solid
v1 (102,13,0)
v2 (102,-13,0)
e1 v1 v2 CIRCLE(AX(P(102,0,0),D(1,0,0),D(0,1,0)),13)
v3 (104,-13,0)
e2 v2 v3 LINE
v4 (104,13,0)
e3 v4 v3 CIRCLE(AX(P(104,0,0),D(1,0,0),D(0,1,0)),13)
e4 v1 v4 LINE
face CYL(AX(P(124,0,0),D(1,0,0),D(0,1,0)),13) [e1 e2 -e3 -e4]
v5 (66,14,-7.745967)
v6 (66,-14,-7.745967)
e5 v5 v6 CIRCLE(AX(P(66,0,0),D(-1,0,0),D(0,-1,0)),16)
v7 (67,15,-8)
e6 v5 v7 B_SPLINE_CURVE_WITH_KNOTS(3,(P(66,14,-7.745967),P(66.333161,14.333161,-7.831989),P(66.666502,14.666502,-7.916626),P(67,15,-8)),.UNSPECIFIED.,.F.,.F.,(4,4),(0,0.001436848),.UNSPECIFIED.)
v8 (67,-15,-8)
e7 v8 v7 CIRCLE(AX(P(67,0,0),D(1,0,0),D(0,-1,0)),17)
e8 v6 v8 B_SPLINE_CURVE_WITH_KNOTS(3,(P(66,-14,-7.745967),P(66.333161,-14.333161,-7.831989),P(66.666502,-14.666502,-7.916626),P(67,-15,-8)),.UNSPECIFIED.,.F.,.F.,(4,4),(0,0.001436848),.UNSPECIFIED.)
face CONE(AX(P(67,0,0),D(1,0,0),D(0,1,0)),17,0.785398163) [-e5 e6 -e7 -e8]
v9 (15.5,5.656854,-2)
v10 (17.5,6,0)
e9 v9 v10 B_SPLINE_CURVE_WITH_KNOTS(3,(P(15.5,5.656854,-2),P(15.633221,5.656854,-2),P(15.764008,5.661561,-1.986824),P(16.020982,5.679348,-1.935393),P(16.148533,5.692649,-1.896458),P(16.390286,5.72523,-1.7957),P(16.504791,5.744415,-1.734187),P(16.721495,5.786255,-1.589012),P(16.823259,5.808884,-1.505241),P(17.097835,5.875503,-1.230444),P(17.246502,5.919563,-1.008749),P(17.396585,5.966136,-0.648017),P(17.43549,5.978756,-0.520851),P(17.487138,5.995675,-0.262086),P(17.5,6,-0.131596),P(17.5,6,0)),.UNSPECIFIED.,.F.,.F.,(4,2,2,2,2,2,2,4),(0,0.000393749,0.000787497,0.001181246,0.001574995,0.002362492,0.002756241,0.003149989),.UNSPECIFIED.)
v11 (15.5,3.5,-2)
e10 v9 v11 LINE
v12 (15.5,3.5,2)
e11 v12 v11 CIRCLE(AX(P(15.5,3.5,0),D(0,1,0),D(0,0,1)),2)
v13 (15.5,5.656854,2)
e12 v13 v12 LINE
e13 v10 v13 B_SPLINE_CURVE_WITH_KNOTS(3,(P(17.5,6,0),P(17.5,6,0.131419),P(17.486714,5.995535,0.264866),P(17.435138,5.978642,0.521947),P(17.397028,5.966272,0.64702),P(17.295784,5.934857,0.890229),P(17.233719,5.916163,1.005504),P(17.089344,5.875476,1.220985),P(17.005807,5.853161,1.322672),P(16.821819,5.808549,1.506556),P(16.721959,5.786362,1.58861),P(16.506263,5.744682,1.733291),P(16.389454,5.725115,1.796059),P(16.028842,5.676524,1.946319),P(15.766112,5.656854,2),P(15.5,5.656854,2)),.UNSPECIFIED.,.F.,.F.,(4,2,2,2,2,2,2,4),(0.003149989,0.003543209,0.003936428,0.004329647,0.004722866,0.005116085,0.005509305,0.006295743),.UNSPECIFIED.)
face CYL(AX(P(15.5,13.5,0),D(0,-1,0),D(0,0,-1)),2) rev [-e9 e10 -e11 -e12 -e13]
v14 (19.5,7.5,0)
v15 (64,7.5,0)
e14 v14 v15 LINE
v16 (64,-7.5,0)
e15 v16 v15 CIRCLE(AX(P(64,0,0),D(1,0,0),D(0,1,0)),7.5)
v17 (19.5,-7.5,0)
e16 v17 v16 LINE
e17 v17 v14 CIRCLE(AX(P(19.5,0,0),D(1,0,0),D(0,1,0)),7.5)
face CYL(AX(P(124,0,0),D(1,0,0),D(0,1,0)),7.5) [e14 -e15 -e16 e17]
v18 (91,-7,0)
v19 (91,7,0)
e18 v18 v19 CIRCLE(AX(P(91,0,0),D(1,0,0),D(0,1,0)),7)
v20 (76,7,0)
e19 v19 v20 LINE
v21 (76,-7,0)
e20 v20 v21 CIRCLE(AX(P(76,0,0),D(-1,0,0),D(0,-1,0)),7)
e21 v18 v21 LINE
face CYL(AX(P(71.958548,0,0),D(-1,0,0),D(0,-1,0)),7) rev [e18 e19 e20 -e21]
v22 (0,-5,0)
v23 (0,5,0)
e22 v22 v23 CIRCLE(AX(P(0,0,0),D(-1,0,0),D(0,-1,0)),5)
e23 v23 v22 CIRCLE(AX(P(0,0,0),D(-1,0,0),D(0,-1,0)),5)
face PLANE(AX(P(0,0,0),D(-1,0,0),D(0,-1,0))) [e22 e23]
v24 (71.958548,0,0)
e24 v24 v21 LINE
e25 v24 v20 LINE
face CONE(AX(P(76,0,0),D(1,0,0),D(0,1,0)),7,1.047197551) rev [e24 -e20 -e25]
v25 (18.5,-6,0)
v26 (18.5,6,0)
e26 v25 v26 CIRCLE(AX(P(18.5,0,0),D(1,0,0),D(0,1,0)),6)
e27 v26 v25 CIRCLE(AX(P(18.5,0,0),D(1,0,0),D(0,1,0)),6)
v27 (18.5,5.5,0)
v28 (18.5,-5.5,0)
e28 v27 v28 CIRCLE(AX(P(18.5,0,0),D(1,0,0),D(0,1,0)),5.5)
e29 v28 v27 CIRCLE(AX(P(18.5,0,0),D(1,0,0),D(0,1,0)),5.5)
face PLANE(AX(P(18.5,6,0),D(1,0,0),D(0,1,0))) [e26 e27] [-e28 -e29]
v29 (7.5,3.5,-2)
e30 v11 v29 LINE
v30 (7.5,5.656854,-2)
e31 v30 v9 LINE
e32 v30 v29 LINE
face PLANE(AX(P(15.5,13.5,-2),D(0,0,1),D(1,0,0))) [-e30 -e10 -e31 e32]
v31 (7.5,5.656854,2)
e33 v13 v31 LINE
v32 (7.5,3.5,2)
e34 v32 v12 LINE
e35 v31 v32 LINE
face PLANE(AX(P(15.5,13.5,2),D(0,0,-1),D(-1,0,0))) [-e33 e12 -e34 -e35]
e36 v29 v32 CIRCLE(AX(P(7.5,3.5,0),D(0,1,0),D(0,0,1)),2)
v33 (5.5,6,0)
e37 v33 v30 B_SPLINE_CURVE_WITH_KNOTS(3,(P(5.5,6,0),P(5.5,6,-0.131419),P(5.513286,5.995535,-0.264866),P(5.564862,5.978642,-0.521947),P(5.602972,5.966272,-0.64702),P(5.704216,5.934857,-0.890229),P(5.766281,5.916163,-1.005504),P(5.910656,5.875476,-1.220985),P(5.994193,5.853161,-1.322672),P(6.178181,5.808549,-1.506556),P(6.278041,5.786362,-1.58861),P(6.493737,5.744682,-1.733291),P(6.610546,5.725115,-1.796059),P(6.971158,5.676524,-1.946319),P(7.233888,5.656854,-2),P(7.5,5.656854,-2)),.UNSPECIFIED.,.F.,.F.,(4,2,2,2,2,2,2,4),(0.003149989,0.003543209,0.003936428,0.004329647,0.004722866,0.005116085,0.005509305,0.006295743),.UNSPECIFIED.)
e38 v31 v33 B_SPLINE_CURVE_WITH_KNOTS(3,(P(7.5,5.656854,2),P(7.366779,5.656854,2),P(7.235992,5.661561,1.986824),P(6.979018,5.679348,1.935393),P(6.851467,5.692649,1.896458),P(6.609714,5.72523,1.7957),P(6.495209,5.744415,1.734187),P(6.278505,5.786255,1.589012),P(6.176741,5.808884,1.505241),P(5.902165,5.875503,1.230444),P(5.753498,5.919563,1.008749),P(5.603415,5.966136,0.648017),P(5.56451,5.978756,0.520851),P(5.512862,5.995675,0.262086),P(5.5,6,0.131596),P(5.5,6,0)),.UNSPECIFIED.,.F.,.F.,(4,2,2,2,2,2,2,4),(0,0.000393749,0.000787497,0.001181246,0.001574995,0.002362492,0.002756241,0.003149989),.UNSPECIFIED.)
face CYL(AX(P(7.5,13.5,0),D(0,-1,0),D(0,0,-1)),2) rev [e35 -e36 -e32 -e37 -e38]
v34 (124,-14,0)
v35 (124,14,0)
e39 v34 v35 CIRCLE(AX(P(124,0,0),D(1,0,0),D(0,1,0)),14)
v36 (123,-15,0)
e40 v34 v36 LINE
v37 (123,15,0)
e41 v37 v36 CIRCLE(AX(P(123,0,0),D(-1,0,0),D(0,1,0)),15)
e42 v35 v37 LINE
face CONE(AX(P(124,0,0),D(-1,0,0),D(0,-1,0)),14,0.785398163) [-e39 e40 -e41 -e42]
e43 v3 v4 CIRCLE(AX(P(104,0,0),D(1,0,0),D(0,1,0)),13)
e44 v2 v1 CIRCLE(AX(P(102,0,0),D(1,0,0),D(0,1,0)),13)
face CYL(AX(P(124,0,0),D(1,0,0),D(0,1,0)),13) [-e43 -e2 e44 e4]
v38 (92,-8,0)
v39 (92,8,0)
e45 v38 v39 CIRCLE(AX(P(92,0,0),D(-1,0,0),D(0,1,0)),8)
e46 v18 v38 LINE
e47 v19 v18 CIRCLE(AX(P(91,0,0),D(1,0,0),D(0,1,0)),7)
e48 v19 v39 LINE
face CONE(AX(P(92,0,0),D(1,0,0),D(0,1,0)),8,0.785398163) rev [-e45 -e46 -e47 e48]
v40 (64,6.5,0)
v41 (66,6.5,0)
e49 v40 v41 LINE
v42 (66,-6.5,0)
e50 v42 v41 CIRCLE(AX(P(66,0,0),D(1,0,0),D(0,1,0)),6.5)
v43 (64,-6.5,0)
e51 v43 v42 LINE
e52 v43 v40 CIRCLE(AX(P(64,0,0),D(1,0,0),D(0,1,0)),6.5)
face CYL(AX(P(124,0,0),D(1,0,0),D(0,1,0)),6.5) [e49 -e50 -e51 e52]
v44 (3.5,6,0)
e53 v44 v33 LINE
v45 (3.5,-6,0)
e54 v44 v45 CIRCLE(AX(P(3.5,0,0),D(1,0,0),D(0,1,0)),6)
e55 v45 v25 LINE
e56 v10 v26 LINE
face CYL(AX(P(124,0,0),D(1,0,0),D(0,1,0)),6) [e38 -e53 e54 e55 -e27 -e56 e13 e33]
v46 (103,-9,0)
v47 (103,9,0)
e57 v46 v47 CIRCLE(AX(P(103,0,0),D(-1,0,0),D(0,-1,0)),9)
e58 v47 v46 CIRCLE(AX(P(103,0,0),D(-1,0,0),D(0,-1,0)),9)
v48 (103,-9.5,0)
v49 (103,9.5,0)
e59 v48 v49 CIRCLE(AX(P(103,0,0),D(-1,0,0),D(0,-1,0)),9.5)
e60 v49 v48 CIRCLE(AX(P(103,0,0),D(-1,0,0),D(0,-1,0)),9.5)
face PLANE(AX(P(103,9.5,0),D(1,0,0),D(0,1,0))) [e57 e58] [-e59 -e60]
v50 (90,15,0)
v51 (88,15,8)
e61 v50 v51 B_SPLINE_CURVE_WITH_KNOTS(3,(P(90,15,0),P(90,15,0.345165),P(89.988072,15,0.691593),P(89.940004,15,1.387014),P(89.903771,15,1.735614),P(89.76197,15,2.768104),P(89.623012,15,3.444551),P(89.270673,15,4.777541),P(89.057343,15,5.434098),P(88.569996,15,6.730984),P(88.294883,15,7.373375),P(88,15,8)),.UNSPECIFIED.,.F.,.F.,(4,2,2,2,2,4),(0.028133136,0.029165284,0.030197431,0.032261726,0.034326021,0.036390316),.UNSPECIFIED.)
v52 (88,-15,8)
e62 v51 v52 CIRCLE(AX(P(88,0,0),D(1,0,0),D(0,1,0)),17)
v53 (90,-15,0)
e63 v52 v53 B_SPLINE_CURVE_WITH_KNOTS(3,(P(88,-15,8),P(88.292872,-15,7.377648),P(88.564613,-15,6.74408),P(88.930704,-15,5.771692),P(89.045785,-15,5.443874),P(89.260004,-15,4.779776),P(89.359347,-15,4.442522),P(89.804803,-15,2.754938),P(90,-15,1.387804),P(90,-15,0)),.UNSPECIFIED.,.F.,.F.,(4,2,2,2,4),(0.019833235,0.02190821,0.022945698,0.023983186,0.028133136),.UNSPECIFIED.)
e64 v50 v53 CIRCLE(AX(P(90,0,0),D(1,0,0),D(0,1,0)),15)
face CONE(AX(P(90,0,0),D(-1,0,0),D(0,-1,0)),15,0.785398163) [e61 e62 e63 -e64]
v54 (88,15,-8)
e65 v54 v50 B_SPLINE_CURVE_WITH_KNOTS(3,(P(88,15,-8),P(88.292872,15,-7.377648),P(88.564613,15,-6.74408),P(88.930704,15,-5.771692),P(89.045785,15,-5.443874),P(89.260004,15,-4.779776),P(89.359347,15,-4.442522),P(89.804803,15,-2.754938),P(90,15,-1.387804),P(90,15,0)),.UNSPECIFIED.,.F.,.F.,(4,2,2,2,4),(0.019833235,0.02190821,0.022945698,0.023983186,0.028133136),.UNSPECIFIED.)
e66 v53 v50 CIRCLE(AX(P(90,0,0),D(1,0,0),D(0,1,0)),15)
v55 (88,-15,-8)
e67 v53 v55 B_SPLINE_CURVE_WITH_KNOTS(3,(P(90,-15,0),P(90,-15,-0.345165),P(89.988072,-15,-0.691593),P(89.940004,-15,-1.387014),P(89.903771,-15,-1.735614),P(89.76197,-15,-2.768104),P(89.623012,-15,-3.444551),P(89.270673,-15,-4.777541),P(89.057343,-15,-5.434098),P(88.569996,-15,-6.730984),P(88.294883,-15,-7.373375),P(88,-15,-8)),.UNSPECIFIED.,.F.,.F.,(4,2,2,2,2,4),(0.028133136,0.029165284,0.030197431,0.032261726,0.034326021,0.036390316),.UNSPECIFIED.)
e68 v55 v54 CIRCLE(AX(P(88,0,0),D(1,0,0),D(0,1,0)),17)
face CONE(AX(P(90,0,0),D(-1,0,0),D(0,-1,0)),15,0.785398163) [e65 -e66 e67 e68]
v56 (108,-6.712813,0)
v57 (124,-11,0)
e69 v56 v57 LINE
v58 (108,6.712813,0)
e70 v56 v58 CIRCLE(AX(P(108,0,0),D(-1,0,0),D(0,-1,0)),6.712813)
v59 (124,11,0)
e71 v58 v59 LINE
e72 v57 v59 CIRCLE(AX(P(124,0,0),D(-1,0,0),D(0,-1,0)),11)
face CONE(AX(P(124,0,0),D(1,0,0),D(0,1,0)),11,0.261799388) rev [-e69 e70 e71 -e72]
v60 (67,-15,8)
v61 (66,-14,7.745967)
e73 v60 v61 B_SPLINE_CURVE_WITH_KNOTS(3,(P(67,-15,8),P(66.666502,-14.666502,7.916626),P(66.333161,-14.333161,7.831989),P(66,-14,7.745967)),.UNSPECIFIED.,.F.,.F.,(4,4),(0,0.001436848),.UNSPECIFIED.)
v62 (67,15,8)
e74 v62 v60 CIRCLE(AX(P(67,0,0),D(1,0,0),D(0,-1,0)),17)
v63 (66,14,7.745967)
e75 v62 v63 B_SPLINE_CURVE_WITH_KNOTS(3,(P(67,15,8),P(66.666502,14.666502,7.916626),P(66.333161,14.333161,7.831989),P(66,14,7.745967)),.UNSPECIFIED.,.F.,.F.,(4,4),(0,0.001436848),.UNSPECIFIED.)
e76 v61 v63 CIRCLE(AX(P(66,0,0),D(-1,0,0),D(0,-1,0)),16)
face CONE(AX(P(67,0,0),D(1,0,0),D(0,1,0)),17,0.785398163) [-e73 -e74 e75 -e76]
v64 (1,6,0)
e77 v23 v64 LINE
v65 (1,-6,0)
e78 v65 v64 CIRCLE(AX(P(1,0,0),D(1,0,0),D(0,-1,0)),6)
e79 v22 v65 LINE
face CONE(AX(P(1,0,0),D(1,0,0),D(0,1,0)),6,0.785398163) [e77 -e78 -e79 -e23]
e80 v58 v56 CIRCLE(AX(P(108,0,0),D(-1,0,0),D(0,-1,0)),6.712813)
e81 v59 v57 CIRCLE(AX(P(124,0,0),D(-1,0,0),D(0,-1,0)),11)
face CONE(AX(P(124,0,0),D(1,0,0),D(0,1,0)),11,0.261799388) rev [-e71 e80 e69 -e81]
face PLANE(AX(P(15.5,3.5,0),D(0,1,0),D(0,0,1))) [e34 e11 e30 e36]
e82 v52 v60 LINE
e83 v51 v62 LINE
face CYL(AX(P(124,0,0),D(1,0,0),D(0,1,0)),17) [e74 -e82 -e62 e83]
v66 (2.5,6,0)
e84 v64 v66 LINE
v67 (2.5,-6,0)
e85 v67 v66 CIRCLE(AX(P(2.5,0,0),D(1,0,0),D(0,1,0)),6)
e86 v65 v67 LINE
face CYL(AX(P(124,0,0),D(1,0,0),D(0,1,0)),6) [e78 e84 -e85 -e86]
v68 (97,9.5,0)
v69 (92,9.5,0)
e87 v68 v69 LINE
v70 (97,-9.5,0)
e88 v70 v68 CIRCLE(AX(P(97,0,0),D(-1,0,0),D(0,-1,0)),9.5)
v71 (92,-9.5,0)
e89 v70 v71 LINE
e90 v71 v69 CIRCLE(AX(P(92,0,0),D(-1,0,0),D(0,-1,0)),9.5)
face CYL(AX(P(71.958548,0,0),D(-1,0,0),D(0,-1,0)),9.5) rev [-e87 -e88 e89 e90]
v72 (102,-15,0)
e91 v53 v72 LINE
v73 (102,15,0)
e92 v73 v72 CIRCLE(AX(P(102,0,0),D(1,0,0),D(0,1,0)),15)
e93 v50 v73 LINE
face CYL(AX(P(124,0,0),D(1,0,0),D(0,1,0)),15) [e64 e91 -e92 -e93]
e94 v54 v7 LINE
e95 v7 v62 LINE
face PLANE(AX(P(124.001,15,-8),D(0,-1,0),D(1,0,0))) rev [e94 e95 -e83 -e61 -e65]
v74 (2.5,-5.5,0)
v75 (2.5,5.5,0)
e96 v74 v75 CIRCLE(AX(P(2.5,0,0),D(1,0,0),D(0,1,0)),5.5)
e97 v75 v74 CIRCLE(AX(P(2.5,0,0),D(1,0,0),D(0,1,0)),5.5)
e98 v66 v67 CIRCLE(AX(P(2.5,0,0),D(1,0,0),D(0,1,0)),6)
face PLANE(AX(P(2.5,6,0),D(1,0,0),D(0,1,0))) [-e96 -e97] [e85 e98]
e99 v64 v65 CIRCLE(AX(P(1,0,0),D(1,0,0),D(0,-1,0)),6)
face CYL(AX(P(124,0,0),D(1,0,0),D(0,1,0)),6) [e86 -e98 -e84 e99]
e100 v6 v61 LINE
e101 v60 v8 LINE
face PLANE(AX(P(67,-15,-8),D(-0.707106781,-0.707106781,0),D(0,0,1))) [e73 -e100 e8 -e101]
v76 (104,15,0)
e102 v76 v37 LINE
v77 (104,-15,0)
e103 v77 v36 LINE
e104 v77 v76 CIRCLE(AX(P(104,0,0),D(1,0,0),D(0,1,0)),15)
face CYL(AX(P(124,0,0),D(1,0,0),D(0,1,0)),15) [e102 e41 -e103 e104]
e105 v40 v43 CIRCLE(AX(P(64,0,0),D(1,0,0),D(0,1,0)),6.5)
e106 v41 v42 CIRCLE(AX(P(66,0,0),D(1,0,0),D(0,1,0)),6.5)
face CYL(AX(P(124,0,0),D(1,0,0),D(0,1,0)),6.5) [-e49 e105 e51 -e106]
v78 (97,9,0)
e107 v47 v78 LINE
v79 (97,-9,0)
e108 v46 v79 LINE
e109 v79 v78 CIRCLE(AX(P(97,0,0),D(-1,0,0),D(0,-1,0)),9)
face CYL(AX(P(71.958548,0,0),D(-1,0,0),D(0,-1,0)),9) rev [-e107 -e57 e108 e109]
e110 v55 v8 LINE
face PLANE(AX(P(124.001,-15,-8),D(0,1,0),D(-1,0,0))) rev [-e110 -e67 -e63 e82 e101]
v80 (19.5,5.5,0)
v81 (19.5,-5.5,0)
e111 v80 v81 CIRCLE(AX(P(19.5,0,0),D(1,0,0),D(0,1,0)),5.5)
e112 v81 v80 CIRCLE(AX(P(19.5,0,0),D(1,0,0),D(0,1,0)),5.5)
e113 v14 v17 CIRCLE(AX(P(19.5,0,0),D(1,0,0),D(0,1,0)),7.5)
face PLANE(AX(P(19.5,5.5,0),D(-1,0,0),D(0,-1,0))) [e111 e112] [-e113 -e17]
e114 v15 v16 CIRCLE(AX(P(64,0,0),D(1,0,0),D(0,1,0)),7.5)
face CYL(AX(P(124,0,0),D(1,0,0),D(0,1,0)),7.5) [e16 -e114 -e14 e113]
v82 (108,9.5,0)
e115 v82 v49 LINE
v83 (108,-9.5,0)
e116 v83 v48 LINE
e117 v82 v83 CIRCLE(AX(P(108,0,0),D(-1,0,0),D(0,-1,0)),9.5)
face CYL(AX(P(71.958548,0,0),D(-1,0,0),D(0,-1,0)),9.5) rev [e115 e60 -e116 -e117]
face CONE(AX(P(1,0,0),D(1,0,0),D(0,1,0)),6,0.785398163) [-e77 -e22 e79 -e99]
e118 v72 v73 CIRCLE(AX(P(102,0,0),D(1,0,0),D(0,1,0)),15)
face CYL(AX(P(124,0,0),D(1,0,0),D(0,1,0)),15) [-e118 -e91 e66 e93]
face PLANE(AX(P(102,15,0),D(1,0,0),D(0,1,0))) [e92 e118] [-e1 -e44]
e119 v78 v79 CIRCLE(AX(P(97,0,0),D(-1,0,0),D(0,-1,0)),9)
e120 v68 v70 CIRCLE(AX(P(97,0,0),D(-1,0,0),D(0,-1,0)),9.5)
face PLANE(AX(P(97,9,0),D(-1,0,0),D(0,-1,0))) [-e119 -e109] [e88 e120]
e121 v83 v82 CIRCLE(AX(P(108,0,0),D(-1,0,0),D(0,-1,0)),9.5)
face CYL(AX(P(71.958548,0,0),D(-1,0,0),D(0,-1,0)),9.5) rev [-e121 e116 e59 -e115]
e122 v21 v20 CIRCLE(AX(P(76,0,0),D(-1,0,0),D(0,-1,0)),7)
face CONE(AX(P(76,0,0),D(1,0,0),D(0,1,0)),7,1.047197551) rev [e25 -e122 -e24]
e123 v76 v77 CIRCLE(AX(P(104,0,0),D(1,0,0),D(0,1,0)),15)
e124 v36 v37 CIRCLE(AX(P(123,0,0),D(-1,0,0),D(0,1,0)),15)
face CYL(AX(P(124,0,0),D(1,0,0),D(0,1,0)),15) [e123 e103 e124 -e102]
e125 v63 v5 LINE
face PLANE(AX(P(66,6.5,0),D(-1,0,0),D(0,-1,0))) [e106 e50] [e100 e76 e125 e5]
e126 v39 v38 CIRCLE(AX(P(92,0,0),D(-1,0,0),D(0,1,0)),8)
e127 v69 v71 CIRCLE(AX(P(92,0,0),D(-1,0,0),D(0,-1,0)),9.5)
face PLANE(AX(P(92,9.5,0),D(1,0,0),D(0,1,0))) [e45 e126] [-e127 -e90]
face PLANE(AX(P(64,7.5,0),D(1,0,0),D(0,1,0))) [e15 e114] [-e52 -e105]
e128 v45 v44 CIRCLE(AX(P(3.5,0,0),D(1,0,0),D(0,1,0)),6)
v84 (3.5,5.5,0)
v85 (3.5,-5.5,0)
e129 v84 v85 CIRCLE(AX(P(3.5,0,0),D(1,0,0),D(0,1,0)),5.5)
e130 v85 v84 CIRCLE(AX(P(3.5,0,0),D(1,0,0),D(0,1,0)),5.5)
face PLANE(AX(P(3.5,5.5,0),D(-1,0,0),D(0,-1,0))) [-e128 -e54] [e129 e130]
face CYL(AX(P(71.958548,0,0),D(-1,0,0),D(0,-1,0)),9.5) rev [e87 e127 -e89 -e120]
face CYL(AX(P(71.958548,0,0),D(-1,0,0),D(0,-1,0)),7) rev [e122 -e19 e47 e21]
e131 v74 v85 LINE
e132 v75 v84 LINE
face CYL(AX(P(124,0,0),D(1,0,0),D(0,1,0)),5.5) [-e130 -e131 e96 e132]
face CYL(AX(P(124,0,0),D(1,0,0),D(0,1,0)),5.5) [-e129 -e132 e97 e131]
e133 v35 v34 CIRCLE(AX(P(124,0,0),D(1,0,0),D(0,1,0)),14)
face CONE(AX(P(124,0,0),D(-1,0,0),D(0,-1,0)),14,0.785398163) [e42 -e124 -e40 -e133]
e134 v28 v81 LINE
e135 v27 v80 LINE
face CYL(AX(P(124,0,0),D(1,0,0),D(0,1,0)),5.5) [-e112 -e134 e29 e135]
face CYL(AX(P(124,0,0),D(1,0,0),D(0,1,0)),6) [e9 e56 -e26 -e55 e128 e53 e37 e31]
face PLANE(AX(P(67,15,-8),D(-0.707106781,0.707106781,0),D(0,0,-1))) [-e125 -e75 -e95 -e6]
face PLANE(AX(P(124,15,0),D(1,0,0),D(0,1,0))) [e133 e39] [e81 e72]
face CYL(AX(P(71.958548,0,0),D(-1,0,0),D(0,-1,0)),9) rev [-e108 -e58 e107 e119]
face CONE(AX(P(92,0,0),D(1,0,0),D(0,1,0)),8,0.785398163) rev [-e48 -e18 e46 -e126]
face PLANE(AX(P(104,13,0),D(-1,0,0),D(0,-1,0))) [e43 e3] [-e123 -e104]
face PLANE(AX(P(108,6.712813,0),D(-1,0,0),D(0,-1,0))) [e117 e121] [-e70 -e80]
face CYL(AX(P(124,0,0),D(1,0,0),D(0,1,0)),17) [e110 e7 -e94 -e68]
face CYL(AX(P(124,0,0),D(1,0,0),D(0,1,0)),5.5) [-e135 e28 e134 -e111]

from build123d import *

# Parameters (mm, degrees)
CUT_EXTRUDE1_START = 3.5
CUT_EXTRUDE1_DEPTH = 10
CUT_EXTRUDE2_REACH = 72.242
CHAMFER1_SIZE      = 1
CHAMFER2_SIZE      = 1


with BuildPart() as part:
    # Sketch1 → Revolve1 (revolve)
    with BuildSketch(Plane.XY):
        Polygon((0, 0), (0, 6), (2.5, 6), (2.5, 5.5), (3.5, 5.5), (3.5, 6), (18.5, 6), (18.5, 5.5), (19.5, 5.5), (19.5, 7.5), (64, 7.5), (64, 6.5), (66, 6.5), (66, 17), (88, 17), (90, 15), (102, 15), (102, 13), (104, 13), (104, 15), (124, 15), (124, 0), align=None)
    revolve(axis=Axis((124, 0, 0), (-1, 0, 0)))

    # Sketch3 → Cut-Extrude1 (cut)
    with BuildSketch(Plane(origin=(0, 0, 0), x_dir=(1, 0, 0), z_dir=(0, 1, 0)).offset(CUT_EXTRUDE1_START)):
        with BuildLine():
            Line((15.5, -2), (7.5, -2))
            ThreePointArc((7.5, -2), (5.5, 0), (7.5, 2))
            Line((7.5, 2), (15.5, 2))
            ThreePointArc((15.5, 2), (17.5, 0), (15.5, -2))
        make_face()
    extrude(amount=CUT_EXTRUDE1_DEPTH, mode=Mode.SUBTRACT)

    # Cut-Extrude2: up to this cone (the profile starts inside it)
    cut_extrude2_end = Plane(origin=(66, 0, 0), z_dir=(-1, 0, 0)).offset(-38.999999) * Cone(1e-06, 150.742, 150.741999, align=(Align.CENTER, Align.CENTER, Align.MIN), mode=Mode.PRIVATE)
    # Sketch6 → Cut-Extrude2 (cut, up to the surface)
    with BuildSketch(Plane.ZY.offset(-66), mode=Mode.PRIVATE) as cut_extrude2_sk1:
        with BuildLine():
            Line((-8, 15), (8, 15))
            ThreePointArc((8, 15), (0, 17), (-8, 15))
        make_face()
    cut_extrude2_tool1 = extrude(cut_extrude2_sk1.sketch, amount=-CUT_EXTRUDE2_REACH, mode=Mode.PRIVATE) & cut_extrude2_end
    add(cut_extrude2_tool1.solids().sort_by_distance((66, 15.804176, 0))[0], mode=Mode.SUBTRACT)
    # Sketch6 → Cut-Extrude2 (cut, up to the surface)
    with BuildSketch(Plane.ZY.offset(-66), mode=Mode.PRIVATE) as cut_extrude2_sk2:
        with BuildLine():
            Line((-8, -15), (8, -15))
            ThreePointArc((8, -15), (0, -17), (-8, -15))
        make_face()
    cut_extrude2_tool2 = extrude(cut_extrude2_sk2.sketch, amount=-CUT_EXTRUDE2_REACH, mode=Mode.PRIVATE) & cut_extrude2_end
    add(cut_extrude2_tool2.solids().sort_by_distance((66, -15.804176, 0))[0], mode=Mode.SUBTRACT)

    # Chamfer1
    chamfer1_edges = [part.edges().sort_by_distance(p)[0] for p in [
        (124, -15, 0),
        (66, 0, 17),
        (0, -6, 0),
        (66, 0, -17),
        (66, 15, 0),
        (66, -15, 0),
    ]]
    chamfer(chamfer1_edges, length=CHAMFER1_SIZE)

    # Sketch7 → Cut-Revolve1 (revolve, cut)
    with BuildSketch(Plane.XY, mode=Mode.PRIVATE) as cut_revolve1_sk:
        Polygon((124, 11), (108, 6.712812921), (108, 9.5), (103, 9.5), (103, 9), (97, 9), (97, 9.5), (92, 9.5), (92, 7), (76, 7), (71.958548116, 0), (124, 0), align=None)
    revolve(cut_revolve1_sk.sketch.rotate(Axis((71.958548116, 0, 0), (1, 0, 0)), 180), axis=Axis((71.958548116, 0, 0), (1, 0, 0)), mode=Mode.SUBTRACT)

    # Chamfer2
    chamfer2_edges = [part.edges().sort_by_distance(p)[0] for p in [
        (92, 7, 0),
    ]]
    chamfer(chamfer2_edges, length=CHAMFER2_SIZE)


solid = part.part
